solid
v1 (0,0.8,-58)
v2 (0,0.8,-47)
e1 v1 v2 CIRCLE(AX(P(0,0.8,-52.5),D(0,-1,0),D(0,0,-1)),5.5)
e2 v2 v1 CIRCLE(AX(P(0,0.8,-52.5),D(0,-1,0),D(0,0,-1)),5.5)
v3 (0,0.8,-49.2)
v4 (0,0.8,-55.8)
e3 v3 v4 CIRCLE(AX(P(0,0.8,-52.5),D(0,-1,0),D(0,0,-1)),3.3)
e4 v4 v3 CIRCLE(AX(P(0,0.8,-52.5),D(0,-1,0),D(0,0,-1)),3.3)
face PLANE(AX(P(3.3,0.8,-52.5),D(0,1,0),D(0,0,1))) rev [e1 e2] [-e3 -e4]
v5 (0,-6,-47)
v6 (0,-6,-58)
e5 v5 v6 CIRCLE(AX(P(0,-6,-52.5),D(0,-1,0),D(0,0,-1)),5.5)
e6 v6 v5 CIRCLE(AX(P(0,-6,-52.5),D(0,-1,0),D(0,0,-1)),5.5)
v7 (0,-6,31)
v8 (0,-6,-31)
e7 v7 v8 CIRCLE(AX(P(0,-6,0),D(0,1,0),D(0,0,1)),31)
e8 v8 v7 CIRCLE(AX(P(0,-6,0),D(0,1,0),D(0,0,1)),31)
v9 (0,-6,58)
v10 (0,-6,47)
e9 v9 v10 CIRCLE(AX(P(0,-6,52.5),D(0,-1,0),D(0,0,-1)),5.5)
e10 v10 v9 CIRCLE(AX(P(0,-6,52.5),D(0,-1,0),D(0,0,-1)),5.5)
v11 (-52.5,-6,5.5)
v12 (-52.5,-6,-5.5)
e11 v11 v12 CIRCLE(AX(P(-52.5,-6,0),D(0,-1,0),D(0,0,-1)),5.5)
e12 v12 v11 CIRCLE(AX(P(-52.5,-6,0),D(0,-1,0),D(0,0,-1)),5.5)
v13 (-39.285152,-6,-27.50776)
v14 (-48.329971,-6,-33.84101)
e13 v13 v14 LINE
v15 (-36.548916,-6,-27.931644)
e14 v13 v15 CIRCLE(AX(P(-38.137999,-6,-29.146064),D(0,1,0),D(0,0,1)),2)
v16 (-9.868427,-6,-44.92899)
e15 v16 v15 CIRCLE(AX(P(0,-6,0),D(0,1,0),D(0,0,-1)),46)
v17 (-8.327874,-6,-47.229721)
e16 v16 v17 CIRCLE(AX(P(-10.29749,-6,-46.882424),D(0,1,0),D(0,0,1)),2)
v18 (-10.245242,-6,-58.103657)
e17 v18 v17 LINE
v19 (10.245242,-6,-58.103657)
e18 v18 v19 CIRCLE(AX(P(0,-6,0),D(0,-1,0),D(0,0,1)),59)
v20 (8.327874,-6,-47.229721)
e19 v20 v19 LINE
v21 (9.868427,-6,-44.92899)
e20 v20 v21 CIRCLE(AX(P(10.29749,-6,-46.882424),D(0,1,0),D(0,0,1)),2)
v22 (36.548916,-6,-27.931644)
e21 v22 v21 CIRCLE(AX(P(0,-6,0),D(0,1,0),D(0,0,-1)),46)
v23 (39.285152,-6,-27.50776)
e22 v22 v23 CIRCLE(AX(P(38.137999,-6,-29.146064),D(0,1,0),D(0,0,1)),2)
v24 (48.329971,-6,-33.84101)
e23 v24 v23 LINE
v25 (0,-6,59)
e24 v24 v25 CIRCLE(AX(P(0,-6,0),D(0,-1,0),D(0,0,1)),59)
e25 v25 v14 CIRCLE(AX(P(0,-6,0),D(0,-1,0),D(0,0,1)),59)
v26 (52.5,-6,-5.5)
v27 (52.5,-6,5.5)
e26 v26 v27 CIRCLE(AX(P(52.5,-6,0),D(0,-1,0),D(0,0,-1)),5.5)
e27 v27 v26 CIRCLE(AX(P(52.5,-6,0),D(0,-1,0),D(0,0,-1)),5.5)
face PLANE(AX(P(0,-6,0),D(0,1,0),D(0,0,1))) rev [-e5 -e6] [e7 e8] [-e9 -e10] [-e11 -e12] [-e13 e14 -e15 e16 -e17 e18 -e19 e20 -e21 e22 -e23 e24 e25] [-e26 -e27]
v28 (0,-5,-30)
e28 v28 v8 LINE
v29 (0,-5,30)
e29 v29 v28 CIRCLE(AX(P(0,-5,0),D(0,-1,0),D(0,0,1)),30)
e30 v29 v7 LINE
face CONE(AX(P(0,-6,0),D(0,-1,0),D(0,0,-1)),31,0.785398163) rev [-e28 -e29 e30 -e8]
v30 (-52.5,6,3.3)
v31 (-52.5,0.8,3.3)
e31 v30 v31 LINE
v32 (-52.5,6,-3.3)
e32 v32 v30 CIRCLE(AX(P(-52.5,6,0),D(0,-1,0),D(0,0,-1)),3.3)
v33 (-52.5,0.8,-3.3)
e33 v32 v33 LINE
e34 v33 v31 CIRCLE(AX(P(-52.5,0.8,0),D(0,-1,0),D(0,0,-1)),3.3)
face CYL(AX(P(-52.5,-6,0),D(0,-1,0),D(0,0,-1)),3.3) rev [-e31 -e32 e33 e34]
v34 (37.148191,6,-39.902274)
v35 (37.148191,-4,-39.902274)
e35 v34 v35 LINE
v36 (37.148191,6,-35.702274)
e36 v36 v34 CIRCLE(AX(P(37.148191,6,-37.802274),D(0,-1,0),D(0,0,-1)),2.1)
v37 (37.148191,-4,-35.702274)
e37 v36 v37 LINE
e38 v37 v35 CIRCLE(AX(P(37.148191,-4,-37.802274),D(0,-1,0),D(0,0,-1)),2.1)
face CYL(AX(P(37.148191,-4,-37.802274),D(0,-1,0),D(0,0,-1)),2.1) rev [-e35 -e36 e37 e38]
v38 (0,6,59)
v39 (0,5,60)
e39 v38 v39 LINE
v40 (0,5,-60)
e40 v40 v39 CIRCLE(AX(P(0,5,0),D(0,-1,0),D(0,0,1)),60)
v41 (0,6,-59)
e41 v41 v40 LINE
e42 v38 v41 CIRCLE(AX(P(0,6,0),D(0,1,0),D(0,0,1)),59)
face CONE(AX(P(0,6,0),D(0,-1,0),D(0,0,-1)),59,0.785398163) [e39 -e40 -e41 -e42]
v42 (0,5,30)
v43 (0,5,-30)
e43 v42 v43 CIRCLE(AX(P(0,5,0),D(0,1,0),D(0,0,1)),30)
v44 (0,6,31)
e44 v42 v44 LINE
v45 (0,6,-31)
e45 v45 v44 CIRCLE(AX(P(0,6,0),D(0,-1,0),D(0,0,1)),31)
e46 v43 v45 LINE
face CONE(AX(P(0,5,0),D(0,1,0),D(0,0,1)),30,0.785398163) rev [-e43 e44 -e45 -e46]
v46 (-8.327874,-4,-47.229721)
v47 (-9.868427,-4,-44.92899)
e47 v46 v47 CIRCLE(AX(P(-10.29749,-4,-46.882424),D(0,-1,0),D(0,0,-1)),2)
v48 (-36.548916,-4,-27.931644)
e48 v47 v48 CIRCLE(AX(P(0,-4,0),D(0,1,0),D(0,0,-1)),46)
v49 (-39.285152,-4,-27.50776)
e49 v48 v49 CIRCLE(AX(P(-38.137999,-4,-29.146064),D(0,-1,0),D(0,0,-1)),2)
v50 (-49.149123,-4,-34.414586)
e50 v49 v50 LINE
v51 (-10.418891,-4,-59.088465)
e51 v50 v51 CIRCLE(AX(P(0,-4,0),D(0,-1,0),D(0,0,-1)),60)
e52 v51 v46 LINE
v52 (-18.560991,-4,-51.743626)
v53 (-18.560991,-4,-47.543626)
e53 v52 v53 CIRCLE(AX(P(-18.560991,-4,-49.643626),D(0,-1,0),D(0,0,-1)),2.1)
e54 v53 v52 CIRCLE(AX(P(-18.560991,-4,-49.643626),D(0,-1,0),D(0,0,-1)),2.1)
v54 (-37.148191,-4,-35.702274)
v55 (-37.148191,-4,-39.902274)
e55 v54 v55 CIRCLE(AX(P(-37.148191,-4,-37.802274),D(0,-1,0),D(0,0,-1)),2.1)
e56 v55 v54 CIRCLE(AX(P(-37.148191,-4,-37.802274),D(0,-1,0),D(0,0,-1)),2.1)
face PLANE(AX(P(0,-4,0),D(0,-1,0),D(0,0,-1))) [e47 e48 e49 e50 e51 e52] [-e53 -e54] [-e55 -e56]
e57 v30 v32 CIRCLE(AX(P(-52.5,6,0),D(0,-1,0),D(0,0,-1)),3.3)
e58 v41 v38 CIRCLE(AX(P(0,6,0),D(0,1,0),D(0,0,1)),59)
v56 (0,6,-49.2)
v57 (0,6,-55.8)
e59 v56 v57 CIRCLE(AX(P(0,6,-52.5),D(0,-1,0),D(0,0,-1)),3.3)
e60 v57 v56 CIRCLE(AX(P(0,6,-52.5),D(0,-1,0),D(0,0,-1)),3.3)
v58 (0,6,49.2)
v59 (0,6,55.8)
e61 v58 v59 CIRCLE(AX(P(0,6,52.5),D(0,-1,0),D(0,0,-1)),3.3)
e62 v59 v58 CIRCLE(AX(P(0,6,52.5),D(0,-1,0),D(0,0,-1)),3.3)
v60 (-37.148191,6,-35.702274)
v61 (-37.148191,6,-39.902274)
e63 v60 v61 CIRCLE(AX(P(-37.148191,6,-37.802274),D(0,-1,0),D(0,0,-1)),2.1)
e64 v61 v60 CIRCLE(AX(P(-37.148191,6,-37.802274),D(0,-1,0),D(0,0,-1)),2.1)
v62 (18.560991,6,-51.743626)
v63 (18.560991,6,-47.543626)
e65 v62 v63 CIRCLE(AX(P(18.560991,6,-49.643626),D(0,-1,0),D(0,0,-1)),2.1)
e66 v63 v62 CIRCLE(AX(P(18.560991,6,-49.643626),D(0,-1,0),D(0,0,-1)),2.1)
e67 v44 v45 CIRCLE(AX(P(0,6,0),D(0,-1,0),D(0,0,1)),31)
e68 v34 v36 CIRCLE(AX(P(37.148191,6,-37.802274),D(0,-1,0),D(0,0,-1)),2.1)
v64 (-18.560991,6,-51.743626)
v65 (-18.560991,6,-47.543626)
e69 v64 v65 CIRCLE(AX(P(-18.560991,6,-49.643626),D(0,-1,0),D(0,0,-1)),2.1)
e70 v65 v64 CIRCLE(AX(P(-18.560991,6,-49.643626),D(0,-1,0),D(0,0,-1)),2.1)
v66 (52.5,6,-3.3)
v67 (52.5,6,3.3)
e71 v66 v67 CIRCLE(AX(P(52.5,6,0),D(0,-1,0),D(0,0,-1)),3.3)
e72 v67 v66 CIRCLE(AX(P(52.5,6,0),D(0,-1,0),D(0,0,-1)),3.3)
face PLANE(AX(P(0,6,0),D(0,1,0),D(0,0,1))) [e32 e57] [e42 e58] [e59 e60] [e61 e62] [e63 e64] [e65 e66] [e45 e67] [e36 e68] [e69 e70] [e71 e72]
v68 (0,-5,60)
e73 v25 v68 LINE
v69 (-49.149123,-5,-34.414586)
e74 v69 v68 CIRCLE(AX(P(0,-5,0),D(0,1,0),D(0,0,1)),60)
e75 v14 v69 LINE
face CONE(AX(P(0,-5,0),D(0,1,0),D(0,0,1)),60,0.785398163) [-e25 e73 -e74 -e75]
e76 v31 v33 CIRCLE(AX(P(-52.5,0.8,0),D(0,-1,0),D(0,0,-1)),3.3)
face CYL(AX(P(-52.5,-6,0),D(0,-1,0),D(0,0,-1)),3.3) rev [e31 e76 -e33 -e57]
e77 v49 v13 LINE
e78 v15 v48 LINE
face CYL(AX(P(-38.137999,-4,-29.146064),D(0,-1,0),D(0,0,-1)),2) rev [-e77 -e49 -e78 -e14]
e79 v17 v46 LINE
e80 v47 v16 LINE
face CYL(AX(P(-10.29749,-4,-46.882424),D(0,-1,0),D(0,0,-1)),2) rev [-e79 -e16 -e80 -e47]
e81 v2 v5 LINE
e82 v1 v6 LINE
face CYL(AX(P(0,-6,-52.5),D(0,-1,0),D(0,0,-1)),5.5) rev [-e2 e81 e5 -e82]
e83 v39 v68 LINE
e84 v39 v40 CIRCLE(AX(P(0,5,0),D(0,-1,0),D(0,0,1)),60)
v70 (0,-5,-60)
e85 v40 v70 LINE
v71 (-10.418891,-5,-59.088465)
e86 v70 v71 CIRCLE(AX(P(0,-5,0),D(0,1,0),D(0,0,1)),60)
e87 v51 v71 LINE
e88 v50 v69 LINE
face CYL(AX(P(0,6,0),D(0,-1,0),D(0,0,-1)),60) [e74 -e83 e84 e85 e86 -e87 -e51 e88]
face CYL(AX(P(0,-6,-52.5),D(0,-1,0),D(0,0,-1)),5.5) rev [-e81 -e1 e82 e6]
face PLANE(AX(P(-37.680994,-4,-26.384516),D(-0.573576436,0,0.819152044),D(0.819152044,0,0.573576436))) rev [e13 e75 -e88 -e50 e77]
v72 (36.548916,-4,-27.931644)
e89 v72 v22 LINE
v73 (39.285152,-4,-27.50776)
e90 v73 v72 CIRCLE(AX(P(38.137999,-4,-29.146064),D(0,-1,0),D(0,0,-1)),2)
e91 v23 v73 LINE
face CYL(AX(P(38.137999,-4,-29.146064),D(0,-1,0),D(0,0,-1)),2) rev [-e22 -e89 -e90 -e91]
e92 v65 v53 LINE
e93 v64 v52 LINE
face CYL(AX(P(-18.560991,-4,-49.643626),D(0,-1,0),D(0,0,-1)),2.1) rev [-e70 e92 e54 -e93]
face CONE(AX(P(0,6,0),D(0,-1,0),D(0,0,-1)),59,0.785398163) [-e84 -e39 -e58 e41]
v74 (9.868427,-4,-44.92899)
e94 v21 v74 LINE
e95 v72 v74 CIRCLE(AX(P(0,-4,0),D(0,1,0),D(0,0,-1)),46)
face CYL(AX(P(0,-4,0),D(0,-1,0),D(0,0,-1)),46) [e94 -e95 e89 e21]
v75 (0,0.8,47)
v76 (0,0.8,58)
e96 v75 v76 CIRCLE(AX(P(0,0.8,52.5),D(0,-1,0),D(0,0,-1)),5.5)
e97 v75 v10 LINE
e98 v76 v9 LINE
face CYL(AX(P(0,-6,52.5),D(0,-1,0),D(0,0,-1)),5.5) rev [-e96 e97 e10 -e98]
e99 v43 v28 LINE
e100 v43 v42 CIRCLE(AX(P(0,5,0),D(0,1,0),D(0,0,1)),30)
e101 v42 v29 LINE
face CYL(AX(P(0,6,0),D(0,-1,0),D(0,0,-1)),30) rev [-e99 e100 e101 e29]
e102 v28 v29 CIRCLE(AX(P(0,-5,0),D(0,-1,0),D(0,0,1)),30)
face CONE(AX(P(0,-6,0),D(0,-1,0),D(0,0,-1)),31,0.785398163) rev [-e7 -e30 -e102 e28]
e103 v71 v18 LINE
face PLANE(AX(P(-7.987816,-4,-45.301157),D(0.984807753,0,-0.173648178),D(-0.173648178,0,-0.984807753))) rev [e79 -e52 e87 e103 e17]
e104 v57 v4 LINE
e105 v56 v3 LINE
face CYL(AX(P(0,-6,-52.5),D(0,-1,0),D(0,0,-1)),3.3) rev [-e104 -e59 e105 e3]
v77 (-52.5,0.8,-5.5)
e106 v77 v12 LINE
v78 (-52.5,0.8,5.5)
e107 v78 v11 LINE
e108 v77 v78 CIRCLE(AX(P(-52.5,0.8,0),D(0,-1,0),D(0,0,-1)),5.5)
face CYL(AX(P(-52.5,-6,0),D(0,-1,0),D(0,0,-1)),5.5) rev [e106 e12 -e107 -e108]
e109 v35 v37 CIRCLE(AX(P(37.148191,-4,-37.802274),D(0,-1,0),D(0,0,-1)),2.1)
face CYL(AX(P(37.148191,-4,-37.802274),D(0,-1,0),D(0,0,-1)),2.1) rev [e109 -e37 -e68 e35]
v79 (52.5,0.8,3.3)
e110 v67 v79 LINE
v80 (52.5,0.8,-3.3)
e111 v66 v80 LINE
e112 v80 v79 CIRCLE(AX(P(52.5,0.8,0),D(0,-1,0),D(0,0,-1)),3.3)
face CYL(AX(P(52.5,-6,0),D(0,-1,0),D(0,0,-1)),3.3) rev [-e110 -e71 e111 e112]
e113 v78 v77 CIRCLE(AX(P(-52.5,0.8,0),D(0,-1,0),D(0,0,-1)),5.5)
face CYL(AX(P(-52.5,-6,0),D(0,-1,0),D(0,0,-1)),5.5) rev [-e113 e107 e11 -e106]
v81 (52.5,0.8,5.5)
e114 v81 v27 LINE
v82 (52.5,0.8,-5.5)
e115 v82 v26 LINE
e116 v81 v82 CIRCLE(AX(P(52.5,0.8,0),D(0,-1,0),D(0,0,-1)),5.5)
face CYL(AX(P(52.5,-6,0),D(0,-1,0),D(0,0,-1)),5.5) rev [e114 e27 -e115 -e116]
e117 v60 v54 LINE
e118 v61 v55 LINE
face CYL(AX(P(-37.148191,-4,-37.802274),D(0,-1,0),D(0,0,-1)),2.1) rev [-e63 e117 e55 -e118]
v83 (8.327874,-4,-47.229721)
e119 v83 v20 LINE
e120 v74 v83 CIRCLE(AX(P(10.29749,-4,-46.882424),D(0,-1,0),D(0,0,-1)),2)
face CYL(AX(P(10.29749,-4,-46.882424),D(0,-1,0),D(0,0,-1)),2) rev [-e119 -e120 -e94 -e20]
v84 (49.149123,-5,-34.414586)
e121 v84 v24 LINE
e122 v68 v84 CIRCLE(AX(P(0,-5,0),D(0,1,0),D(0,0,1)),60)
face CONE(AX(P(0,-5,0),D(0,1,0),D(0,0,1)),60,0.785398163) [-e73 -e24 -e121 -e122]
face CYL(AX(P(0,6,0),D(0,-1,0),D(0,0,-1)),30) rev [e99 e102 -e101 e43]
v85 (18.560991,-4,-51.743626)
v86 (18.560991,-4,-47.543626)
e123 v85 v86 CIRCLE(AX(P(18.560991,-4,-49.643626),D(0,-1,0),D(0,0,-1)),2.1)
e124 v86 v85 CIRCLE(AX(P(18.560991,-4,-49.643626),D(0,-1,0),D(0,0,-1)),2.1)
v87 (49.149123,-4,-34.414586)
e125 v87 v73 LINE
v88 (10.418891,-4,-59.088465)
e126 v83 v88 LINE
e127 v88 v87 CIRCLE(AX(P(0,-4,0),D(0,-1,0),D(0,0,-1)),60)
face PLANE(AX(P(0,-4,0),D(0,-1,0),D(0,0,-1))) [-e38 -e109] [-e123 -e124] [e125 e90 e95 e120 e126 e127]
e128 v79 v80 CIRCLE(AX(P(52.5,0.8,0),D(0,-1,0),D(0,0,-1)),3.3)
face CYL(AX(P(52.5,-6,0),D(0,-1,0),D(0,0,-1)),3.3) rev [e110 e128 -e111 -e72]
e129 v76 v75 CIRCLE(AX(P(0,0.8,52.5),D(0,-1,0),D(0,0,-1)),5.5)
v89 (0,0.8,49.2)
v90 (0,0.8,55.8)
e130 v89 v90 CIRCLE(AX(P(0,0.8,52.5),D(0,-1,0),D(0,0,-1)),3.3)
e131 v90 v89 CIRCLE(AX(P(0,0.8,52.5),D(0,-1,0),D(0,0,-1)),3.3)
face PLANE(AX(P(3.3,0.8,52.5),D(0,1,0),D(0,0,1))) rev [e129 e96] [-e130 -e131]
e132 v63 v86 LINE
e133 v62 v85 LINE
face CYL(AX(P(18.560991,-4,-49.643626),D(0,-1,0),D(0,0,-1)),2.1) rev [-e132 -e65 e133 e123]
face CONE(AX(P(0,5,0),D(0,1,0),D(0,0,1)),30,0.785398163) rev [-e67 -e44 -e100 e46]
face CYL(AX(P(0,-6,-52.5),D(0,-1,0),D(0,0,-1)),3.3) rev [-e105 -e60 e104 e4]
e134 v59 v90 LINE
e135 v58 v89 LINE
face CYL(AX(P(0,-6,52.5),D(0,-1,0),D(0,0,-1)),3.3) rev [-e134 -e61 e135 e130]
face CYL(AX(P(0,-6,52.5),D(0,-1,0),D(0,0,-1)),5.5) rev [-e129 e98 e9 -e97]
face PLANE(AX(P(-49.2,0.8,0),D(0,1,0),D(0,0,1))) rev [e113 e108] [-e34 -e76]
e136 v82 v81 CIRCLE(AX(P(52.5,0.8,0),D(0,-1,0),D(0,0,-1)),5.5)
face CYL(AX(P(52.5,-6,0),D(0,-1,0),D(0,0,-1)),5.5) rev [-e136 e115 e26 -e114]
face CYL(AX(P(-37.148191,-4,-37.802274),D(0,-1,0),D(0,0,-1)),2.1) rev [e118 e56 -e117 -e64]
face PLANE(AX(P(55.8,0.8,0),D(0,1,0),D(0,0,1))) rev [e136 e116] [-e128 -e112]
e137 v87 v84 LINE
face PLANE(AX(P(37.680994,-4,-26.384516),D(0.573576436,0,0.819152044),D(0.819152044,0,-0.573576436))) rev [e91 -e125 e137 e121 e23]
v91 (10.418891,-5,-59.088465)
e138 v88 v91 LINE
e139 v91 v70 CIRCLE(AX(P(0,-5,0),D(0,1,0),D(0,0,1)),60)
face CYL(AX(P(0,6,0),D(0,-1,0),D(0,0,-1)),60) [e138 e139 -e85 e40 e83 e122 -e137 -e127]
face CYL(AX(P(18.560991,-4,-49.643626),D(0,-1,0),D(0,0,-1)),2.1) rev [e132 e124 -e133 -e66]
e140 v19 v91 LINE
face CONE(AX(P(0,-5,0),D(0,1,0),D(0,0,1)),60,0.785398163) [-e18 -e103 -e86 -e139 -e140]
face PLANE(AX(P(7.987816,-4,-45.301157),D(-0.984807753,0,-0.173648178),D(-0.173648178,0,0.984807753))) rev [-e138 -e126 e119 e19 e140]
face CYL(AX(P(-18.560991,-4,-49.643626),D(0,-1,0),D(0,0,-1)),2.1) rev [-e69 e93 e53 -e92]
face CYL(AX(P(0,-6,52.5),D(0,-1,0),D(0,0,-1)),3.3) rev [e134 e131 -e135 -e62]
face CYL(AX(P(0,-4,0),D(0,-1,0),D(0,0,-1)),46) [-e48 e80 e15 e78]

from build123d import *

# Parameters (mm, degrees)
SKETCH1_R                                            = 60
SKETCH1_R_2                                          = 30
BOSS_EXTRUDE1_DEPTH                                  = 6
CHAMFER1_SIZE                                        = 1
HOLE_SIZE_BY_SOCKET_HEAD_CAP_SCREW_TYPE1_D           = 6.6
HOLE_SIZE_BY_SOCKET_HEAD_CAP_SCREW_TYPE1_CBORE_D     = 11
HOLE_SIZE_BY_SOCKET_HEAD_CAP_SCREW_TYPE1_CBORE_DEPTH = 6.8
CUT_EXTRUDE1_START                                   = -2
CUT_EXTRUDE1_DEPTH                                   = 2
FILLET1_R                                            = 2
M5_TAPPED_HOLE1_D                                    = 4.2


with BuildPart() as part:
    # Sketch1 → Boss-Extrude1 (new, symmetric)
    with BuildSketch(Plane(origin=(0, 0, 0), x_dir=(1, 0, 0), z_dir=(0, 1, 0))):
        with Locations(Location((0, 0, 0), (0, 0, 270))):
            Circle(SKETCH1_R)
        with Locations(Location((0, 0, 0), (0, 0, 270))):
            Circle(SKETCH1_R_2, mode=Mode.SUBTRACT)
    extrude(amount=BOSS_EXTRUDE1_DEPTH, both=True)

    # Chamfer1
    chamfer1_edges = [part.edges().sort_by_distance(p)[0] for p in [
        (0, -6, -60),
        (0, 6, -60),
        (0, -6, -30),
        (0, 6, -30),
    ]]
    chamfer(chamfer1_edges, length=CHAMFER1_SIZE)

    # Hole Size by Socket Head Cap Screw Type1 (through all)
    with Locations(Plane(origin=(-41.126423616, -6, 15.006070464), x_dir=(1, 0, 0), z_dir=(0, -1, 0))):
        with Locations((-11.373576384, -15.006070464), (93.626423616, -15.006070464), (41.126423616, -67.506070464), (41.126423616, 37.493929536)):
            CounterBoreHole(HOLE_SIZE_BY_SOCKET_HEAD_CAP_SCREW_TYPE1_D / 2, HOLE_SIZE_BY_SOCKET_HEAD_CAP_SCREW_TYPE1_CBORE_D / 2, HOLE_SIZE_BY_SOCKET_HEAD_CAP_SCREW_TYPE1_CBORE_DEPTH)

    # Sketch4 → Cut-Extrude1 (cut)
    with BuildSketch(Plane.XZ.offset(6).offset(CUT_EXTRUDE1_START)):
        with BuildLine():
            Line((-37.680994037, -26.384516072), (-49.149122657, -34.414586181))
            ThreePointArc((-49.149122657, -34.414586181), (-32.237976501, -50.603486749), (-10.41889066, -59.088465181))
            Line((-10.41889066, -59.088465181), (-7.987816173, -45.301156639))
            ThreePointArc((-7.987816173, -45.301156639), (-24.715781984, -38.796006507), (-37.680994037, -26.384516072))
        make_face()
        with BuildLine():
            Line((7.987816173, -45.301156639), (10.41889066, -59.088465181))
            ThreePointArc((10.41889066, -59.088465181), (32.237976501, -50.603486749), (49.149122657, -34.414586181))
            Line((49.149122657, -34.414586181), (37.680994037, -26.384516072))
            ThreePointArc((37.680994037, -26.384516072), (24.715781984, -38.796006507), (7.987816173, -45.301156639))
        make_face()
    extrude(amount=CUT_EXTRUDE1_DEPTH, mode=Mode.SUBTRACT)

    # Fillet1
    fillet1_edges = [part.edges().sort_by_distance(p)[0] for p in [
        (-37.680994037, -5, -26.384516072),
        (-7.987816173, -5, -45.301156639),
        (7.987816173, -5, -45.301156639),
        (37.680994037, -5, -26.384516072),
    ]]
    fillet(fillet1_edges, radius=FILLET1_R)

    # M5 Tapped Hole1 (through all)
    with Locations(Plane(origin=(0, -4, 0), x_dir=(-1, 0, 0), z_dir=(0, -1, 0))):
        with Locations((37.148191008, 37.802273805), (18.560991207, 49.64362603), (-18.560991207, 49.64362603), (-37.148191008, 37.802273805)):
            Hole(M5_TAPPED_HOLE1_D / 2)


solid = part.part
